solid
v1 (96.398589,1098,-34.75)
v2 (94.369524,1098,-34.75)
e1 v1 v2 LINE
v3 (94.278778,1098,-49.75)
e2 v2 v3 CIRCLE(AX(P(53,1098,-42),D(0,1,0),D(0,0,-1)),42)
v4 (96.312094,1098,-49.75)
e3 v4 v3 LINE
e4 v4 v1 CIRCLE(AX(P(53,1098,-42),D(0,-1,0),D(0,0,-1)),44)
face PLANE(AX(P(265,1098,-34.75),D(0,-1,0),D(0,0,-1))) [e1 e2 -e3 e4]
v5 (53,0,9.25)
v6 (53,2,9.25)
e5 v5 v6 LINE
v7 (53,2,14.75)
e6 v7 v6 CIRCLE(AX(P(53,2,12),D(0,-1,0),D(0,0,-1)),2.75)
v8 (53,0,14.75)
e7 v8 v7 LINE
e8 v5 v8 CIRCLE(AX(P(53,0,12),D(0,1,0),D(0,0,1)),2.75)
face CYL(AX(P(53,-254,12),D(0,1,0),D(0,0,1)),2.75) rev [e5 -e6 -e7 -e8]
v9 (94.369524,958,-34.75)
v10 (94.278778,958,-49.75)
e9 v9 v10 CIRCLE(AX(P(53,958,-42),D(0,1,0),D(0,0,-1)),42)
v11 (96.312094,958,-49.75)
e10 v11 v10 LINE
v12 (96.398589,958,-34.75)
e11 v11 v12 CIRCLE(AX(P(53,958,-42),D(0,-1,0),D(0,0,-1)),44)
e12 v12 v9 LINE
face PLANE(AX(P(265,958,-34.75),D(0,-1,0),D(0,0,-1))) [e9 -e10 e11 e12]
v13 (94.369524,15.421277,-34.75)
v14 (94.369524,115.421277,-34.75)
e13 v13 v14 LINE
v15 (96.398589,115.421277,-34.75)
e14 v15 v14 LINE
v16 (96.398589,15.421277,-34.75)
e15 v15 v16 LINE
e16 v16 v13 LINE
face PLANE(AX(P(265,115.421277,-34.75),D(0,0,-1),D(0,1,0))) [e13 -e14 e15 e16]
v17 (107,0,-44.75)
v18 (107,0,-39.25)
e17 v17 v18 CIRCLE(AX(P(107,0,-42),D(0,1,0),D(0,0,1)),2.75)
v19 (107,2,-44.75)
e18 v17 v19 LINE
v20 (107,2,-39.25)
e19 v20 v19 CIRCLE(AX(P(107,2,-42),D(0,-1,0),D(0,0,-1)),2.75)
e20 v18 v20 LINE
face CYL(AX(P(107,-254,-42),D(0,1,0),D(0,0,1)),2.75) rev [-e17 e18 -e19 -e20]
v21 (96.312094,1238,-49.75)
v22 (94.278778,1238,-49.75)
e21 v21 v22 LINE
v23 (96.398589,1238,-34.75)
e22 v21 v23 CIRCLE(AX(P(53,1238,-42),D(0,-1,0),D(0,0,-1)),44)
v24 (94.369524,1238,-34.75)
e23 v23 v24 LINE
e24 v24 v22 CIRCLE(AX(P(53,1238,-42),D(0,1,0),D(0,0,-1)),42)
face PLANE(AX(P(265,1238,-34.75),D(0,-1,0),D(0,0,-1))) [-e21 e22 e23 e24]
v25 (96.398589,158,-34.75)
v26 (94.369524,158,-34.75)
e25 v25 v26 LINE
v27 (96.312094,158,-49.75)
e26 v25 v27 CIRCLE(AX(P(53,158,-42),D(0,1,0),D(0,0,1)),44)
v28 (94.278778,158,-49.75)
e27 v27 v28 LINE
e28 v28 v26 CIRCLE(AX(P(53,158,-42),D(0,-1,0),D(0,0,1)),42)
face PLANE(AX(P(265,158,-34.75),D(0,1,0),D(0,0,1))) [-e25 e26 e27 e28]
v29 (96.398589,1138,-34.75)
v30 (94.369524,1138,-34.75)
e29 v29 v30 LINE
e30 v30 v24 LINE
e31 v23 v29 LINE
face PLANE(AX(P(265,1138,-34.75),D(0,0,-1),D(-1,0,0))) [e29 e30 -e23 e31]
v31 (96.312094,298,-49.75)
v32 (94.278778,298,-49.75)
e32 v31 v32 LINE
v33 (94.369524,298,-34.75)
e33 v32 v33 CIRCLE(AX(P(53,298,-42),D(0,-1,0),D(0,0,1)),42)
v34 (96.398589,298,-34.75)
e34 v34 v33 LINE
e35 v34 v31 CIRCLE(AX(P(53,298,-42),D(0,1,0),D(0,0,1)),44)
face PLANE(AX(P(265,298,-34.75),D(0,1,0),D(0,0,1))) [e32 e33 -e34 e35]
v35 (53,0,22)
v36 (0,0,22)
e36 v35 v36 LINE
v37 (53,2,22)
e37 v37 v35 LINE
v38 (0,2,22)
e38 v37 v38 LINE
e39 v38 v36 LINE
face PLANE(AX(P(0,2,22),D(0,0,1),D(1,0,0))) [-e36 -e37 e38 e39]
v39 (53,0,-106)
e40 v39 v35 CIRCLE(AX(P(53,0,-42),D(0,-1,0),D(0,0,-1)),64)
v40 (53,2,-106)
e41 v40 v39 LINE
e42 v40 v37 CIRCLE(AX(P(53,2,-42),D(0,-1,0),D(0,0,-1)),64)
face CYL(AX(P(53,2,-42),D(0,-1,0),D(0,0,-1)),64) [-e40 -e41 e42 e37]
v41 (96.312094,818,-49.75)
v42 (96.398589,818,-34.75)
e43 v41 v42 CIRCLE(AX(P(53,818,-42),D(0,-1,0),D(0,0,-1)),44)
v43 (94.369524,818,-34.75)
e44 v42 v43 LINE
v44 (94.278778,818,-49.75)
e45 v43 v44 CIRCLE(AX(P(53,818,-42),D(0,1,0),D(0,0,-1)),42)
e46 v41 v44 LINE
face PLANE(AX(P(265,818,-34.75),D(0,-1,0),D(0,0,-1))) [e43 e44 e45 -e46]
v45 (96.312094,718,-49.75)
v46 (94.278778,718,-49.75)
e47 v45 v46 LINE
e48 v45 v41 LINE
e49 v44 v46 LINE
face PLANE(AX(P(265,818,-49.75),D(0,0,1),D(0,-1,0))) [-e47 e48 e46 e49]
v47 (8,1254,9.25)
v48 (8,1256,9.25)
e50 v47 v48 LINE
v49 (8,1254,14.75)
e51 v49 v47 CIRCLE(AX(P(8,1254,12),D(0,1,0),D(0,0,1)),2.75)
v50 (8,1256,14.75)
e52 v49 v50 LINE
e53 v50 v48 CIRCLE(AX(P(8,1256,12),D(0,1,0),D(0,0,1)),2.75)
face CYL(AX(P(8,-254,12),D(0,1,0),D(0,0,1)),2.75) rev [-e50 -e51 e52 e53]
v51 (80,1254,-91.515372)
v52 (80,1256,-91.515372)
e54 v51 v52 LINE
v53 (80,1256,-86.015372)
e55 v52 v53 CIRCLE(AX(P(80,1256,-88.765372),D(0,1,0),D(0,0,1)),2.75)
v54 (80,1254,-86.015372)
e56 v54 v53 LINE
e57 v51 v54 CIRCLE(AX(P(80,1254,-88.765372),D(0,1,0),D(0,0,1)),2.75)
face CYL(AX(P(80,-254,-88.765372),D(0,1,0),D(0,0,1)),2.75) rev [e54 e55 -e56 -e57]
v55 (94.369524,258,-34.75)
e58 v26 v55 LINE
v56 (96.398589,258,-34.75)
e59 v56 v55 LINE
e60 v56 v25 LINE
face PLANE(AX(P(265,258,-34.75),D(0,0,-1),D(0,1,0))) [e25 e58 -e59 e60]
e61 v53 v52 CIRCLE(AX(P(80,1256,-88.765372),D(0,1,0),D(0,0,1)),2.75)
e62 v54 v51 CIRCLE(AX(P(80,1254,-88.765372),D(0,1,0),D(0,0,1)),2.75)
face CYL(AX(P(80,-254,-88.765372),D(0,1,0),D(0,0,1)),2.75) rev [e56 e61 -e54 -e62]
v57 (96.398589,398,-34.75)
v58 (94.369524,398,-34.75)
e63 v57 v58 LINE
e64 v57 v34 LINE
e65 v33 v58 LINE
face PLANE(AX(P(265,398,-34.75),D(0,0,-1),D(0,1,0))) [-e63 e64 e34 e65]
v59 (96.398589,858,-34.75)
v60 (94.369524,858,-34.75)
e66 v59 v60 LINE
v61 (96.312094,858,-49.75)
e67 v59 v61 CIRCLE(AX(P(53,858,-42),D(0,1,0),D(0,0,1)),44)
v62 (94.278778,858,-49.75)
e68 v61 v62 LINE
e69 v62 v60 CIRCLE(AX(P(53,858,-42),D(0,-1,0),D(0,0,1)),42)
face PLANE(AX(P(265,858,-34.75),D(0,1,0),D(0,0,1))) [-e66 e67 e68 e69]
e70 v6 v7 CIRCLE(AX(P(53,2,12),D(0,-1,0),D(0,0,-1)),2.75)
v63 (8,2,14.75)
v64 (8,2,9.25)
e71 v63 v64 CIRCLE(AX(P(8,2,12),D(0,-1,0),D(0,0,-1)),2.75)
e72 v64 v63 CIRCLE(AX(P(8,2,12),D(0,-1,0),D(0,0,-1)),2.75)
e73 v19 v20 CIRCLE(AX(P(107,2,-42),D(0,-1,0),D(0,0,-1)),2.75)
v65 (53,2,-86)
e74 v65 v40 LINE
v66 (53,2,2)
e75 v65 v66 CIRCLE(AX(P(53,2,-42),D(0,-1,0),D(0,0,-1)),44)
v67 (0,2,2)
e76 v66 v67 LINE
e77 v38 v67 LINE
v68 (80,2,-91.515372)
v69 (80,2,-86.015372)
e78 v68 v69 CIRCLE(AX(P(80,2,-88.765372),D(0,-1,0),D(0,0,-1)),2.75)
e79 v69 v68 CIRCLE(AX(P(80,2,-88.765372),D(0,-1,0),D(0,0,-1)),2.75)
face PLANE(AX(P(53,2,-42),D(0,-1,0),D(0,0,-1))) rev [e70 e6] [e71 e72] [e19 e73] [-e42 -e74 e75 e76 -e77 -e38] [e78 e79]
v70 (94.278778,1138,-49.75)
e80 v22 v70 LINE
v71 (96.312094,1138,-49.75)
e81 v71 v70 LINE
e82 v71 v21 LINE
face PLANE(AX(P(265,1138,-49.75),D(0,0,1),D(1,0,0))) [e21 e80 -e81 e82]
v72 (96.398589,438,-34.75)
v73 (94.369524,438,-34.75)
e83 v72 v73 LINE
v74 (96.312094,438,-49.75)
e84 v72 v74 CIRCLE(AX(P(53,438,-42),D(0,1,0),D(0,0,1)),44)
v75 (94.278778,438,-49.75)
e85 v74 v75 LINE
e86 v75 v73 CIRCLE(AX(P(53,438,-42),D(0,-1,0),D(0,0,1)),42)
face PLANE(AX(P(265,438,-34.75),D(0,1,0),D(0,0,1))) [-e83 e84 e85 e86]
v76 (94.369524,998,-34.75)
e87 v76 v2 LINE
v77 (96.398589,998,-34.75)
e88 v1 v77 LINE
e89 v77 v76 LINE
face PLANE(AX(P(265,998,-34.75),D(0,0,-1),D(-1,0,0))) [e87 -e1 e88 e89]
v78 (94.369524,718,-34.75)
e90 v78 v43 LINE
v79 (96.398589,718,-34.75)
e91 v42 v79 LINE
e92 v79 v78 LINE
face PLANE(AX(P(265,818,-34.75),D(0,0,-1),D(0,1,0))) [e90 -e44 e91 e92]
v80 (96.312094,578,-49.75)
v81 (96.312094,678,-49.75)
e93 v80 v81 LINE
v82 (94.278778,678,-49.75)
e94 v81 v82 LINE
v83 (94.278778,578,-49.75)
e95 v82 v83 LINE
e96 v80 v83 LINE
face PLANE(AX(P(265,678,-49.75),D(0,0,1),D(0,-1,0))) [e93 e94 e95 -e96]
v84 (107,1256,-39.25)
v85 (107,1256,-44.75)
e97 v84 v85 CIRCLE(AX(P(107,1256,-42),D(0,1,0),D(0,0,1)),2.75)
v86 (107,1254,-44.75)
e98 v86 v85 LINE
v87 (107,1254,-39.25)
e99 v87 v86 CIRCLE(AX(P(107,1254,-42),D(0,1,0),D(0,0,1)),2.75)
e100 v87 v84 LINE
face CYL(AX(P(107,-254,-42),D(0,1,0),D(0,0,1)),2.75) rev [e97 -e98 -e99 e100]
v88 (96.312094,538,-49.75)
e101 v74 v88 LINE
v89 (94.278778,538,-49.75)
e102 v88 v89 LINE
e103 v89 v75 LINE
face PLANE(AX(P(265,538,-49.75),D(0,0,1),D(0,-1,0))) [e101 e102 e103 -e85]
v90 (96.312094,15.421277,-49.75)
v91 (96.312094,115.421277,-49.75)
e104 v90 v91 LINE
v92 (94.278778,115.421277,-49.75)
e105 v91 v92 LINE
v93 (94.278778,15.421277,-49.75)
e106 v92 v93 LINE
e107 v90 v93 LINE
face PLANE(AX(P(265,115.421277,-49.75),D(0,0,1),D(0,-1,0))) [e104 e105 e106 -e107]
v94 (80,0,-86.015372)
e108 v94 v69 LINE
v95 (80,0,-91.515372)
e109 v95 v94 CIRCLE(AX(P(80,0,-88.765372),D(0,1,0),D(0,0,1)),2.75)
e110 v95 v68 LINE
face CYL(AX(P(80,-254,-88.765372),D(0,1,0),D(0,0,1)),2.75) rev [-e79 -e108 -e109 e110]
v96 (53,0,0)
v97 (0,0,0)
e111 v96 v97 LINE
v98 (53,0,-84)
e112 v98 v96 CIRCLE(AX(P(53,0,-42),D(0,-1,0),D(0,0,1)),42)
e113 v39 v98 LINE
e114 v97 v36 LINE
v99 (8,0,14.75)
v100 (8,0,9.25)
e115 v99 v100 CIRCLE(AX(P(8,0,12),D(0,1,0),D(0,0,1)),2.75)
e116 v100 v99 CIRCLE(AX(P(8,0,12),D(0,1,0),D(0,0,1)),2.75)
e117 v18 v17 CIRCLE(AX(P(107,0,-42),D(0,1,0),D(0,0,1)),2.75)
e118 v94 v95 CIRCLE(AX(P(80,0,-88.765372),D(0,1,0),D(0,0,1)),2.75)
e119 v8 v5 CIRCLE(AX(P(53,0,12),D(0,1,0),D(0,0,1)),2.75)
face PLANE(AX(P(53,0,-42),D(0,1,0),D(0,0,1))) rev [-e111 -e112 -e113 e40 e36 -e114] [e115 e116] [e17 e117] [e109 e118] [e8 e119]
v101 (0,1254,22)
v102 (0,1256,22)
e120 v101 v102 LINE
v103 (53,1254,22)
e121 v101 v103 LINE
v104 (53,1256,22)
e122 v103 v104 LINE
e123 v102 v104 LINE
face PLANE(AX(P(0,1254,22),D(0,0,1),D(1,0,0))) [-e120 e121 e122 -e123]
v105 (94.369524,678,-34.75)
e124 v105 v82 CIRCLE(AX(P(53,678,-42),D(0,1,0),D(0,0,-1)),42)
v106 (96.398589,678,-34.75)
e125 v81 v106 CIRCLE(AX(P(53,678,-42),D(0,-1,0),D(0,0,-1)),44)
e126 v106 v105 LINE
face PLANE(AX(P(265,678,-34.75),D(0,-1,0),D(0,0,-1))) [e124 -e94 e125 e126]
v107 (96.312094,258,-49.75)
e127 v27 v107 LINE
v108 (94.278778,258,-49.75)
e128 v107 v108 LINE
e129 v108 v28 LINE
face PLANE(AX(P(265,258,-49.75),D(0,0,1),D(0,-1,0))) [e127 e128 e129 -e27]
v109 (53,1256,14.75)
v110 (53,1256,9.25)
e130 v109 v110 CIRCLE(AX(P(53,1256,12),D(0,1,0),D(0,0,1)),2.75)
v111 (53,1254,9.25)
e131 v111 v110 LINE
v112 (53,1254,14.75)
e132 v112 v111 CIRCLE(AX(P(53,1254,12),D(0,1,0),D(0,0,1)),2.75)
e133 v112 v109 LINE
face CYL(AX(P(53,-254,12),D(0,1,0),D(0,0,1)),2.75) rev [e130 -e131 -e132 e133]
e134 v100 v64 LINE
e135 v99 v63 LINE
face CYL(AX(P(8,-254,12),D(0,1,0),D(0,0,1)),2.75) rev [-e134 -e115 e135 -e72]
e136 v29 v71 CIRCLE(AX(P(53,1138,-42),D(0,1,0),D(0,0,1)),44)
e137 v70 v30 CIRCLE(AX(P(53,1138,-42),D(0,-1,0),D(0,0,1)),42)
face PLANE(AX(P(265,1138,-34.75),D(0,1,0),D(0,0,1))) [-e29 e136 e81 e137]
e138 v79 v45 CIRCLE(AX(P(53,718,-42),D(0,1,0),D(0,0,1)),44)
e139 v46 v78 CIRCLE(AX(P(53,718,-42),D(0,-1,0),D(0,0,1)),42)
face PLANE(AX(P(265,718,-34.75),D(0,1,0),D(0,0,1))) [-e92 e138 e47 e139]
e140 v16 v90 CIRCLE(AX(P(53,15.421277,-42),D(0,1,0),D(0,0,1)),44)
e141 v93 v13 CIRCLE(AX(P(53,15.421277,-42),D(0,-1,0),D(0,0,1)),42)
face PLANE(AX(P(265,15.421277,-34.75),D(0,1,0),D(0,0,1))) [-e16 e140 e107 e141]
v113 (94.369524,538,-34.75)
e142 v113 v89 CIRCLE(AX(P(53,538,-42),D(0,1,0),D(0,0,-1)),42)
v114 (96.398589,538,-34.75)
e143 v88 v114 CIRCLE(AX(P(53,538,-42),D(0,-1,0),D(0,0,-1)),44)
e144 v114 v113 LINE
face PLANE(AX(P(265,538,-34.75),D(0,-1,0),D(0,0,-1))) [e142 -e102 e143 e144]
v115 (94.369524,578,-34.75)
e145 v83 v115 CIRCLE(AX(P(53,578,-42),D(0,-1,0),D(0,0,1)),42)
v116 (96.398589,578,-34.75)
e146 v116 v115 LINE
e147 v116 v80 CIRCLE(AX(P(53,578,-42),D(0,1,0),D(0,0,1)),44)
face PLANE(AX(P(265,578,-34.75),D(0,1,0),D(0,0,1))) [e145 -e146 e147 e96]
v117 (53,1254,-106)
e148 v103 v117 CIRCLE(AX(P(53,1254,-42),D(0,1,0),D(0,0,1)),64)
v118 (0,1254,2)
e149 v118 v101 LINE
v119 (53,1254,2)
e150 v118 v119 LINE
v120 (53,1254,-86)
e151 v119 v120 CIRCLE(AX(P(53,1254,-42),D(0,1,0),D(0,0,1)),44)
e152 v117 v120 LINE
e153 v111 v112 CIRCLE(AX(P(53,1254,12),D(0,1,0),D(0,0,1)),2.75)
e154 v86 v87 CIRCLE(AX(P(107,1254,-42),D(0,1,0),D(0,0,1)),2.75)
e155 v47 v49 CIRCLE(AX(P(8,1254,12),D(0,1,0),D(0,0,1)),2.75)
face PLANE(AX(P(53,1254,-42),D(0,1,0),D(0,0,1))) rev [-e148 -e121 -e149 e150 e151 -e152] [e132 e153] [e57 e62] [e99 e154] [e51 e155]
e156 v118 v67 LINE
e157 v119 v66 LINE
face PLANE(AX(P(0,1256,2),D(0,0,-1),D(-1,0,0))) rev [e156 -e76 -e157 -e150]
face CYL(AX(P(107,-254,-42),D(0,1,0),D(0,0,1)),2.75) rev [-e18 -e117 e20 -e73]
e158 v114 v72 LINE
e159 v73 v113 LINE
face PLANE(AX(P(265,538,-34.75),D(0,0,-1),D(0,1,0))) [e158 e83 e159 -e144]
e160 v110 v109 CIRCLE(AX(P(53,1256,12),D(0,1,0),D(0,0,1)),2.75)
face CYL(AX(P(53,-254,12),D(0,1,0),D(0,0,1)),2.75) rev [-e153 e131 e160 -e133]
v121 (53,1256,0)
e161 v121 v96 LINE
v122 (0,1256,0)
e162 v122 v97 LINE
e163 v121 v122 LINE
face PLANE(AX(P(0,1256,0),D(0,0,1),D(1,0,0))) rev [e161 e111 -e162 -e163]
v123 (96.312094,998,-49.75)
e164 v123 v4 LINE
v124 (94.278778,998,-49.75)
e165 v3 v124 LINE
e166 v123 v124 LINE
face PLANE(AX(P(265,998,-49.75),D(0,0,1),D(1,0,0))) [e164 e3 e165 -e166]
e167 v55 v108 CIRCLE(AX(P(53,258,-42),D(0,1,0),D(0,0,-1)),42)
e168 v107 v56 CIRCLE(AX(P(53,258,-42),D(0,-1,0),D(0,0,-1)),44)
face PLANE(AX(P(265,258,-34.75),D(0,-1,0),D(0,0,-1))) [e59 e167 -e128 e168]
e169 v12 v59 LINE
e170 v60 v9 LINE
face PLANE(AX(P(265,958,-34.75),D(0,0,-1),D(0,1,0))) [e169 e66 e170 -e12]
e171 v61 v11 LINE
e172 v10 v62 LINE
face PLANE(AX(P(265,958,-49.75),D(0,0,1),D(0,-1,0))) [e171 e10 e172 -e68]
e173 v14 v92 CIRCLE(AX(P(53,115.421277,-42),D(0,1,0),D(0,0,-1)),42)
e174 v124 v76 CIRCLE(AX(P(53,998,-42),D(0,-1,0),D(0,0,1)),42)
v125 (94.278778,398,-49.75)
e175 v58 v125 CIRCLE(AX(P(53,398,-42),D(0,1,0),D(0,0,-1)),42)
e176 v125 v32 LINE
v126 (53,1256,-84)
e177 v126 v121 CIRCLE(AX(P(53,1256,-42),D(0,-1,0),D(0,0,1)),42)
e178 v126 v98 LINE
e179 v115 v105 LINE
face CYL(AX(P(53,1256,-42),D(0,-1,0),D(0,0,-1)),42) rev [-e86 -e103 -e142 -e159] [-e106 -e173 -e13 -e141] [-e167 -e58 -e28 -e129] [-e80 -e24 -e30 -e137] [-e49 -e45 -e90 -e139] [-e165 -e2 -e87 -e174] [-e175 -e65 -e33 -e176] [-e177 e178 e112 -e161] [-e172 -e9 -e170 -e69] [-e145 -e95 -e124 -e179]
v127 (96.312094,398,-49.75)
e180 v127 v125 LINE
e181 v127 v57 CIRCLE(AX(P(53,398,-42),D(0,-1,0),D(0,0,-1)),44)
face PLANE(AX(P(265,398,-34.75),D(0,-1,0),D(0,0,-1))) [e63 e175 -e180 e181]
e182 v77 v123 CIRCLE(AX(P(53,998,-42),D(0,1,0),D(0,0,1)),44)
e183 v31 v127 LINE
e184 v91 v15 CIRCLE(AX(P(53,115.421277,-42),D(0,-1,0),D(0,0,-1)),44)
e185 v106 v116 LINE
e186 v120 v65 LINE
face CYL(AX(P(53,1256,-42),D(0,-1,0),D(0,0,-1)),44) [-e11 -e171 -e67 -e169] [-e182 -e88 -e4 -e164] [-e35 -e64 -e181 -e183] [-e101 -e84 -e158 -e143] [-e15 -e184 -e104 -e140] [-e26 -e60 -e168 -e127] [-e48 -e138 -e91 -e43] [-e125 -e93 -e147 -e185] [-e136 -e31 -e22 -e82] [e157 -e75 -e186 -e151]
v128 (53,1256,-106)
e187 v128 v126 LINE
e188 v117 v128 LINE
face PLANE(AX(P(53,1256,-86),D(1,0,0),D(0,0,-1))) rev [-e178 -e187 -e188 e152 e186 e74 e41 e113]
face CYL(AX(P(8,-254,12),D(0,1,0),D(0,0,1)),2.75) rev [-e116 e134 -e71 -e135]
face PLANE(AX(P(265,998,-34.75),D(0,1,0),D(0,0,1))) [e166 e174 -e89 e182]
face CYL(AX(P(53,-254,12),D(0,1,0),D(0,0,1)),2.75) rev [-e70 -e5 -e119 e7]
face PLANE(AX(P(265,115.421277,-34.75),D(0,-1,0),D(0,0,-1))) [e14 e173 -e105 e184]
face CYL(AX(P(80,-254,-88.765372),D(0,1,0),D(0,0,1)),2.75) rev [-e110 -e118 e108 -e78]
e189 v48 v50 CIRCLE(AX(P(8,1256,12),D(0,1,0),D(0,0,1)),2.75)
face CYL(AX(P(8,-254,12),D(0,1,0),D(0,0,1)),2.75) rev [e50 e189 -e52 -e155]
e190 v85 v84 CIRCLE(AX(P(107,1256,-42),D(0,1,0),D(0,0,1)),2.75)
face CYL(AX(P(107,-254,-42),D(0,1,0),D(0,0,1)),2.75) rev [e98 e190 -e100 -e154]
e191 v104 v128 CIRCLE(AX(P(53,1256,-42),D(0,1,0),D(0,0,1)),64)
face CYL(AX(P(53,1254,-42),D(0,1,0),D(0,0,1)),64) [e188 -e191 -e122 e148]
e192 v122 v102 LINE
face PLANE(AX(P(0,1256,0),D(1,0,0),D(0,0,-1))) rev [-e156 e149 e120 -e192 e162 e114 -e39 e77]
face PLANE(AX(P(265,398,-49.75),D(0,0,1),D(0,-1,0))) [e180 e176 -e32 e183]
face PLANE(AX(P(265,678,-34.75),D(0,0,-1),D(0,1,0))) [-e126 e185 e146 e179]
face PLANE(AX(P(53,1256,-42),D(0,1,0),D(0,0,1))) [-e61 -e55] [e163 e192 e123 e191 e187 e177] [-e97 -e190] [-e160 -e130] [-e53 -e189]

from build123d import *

# Parameters (mm, degrees)
EXTRUDE_1_DEPTH     = 1256
EXTRUDE_START       = -2
EXTRUDE_2_DEPTH     = 2
EXTRUDE_3_DEPTH     = 2
SKETCH_5_W          = 15
SKETCH_5_H          = 100
CUT_EXTRUDE_2_DEPTH = 265
SKETCH_6_R          = 2.75
CUT_EXTRUDE_3_DEPTH = 1510


with BuildPart() as part:
    # 草图1 → 凸台-拉伸1 (new body)
    with BuildSketch(Plane(origin=(0, 0, 0), x_dir=(1, 0, 0), z_dir=(0, 1, 0))):
        with BuildLine():
            Line((0, 0), (53, 0))
            ThreePointArc((53, 0), (95, 42), (53, 84))
            Line((53, 84), (53, 86))
            ThreePointArc((53, 86), (97, 42), (53, -2))
            Line((53, -2), (0, -2))
            Line((0, -2), (0, 0))
        make_face()
    extrude(amount=EXTRUDE_1_DEPTH)

    # 草图3 → 凸台-拉伸2 (add)
    with BuildSketch(Plane(origin=(0, 1256, 0), x_dir=(1, 0, 0), z_dir=(0, 1, 0)).offset(EXTRUDE_START)):
        with BuildLine():
            Line((0, 0), (53, 0))
            ThreePointArc((53, 0), (95, 42), (53, 84))
            Line((53, 84), (53, 106))
            ThreePointArc((53, 106), (117, 42), (53, -22))
            Line((53, -22), (0, -22))
            Line((0, -22), (0, 0))
        make_face()
    extrude(amount=EXTRUDE_2_DEPTH)

    # 草图4 → 凸台-拉伸3 (add)
    with BuildSketch(Plane.XZ):
        with BuildLine():
            Line((53, 0), (0, 0))
            Line((0, 0), (0, 2))
            Line((0, 2), (0, 22))
            Line((0, 22), (53, 22))
            ThreePointArc((53, 22), (117, -42), (53, -106))
            Line((53, -106), (53, -86))
            Line((53, -86), (53, -84))
            ThreePointArc((53, -84), (95, -42), (53, 0))
        make_face()
    extrude(amount=-EXTRUDE_3_DEPTH)

    # 草图5 → 切除-拉伸2 (cut)
    with BuildSketch(Plane(origin=(0, 0, 0), x_dir=(0, 0, -1), z_dir=(1, 0, 0))):
        with Locations((42.25, 65.421277154)):
            Rectangle(SKETCH_5_W, SKETCH_5_H)
        with Locations((42.25, 208)):
            Rectangle(SKETCH_5_W, SKETCH_5_H)
        with Locations((42.25, 1048)):
            Rectangle(SKETCH_5_W, SKETCH_5_H)
        with Locations((42.25, 348)):
            Rectangle(SKETCH_5_W, SKETCH_5_H)
        with Locations((42.25, 488)):
            Rectangle(SKETCH_5_W, SKETCH_5_H)
        with Locations((42.25, 628)):
            Rectangle(SKETCH_5_W, SKETCH_5_H)
        with Locations((42.25, 768)):
            Rectangle(SKETCH_5_W, SKETCH_5_H)
        with Locations((42.25, 908)):
            Rectangle(SKETCH_5_W, SKETCH_5_H)
        with Locations((42.25, 1188)):
            Rectangle(SKETCH_5_W, SKETCH_5_H)
    extrude(amount=CUT_EXTRUDE_2_DEPTH, mode=Mode.SUBTRACT)

    # 草图6 → 切除-拉伸3 (cut)
    with BuildSketch(Plane(origin=(0, 1256, 0), x_dir=(1, 0, 0), z_dir=(0, 1, 0))):
        with Locations(Location((80, 88.765371804, 0), (0, 0, 270))):
            Circle(SKETCH_6_R)
        with Locations(Location((107, 42, 0), (0, 0, 270))):
            Circle(SKETCH_6_R)
        with Locations(Location((53, -12, 0), (0, 0, 270))):
            Circle(SKETCH_6_R)
        with Locations(Location((8, -12, 0), (0, 0, 270))):
            Circle(SKETCH_6_R)
    extrude(amount=-CUT_EXTRUDE_3_DEPTH, mode=Mode.SUBTRACT)


solid = part.part
